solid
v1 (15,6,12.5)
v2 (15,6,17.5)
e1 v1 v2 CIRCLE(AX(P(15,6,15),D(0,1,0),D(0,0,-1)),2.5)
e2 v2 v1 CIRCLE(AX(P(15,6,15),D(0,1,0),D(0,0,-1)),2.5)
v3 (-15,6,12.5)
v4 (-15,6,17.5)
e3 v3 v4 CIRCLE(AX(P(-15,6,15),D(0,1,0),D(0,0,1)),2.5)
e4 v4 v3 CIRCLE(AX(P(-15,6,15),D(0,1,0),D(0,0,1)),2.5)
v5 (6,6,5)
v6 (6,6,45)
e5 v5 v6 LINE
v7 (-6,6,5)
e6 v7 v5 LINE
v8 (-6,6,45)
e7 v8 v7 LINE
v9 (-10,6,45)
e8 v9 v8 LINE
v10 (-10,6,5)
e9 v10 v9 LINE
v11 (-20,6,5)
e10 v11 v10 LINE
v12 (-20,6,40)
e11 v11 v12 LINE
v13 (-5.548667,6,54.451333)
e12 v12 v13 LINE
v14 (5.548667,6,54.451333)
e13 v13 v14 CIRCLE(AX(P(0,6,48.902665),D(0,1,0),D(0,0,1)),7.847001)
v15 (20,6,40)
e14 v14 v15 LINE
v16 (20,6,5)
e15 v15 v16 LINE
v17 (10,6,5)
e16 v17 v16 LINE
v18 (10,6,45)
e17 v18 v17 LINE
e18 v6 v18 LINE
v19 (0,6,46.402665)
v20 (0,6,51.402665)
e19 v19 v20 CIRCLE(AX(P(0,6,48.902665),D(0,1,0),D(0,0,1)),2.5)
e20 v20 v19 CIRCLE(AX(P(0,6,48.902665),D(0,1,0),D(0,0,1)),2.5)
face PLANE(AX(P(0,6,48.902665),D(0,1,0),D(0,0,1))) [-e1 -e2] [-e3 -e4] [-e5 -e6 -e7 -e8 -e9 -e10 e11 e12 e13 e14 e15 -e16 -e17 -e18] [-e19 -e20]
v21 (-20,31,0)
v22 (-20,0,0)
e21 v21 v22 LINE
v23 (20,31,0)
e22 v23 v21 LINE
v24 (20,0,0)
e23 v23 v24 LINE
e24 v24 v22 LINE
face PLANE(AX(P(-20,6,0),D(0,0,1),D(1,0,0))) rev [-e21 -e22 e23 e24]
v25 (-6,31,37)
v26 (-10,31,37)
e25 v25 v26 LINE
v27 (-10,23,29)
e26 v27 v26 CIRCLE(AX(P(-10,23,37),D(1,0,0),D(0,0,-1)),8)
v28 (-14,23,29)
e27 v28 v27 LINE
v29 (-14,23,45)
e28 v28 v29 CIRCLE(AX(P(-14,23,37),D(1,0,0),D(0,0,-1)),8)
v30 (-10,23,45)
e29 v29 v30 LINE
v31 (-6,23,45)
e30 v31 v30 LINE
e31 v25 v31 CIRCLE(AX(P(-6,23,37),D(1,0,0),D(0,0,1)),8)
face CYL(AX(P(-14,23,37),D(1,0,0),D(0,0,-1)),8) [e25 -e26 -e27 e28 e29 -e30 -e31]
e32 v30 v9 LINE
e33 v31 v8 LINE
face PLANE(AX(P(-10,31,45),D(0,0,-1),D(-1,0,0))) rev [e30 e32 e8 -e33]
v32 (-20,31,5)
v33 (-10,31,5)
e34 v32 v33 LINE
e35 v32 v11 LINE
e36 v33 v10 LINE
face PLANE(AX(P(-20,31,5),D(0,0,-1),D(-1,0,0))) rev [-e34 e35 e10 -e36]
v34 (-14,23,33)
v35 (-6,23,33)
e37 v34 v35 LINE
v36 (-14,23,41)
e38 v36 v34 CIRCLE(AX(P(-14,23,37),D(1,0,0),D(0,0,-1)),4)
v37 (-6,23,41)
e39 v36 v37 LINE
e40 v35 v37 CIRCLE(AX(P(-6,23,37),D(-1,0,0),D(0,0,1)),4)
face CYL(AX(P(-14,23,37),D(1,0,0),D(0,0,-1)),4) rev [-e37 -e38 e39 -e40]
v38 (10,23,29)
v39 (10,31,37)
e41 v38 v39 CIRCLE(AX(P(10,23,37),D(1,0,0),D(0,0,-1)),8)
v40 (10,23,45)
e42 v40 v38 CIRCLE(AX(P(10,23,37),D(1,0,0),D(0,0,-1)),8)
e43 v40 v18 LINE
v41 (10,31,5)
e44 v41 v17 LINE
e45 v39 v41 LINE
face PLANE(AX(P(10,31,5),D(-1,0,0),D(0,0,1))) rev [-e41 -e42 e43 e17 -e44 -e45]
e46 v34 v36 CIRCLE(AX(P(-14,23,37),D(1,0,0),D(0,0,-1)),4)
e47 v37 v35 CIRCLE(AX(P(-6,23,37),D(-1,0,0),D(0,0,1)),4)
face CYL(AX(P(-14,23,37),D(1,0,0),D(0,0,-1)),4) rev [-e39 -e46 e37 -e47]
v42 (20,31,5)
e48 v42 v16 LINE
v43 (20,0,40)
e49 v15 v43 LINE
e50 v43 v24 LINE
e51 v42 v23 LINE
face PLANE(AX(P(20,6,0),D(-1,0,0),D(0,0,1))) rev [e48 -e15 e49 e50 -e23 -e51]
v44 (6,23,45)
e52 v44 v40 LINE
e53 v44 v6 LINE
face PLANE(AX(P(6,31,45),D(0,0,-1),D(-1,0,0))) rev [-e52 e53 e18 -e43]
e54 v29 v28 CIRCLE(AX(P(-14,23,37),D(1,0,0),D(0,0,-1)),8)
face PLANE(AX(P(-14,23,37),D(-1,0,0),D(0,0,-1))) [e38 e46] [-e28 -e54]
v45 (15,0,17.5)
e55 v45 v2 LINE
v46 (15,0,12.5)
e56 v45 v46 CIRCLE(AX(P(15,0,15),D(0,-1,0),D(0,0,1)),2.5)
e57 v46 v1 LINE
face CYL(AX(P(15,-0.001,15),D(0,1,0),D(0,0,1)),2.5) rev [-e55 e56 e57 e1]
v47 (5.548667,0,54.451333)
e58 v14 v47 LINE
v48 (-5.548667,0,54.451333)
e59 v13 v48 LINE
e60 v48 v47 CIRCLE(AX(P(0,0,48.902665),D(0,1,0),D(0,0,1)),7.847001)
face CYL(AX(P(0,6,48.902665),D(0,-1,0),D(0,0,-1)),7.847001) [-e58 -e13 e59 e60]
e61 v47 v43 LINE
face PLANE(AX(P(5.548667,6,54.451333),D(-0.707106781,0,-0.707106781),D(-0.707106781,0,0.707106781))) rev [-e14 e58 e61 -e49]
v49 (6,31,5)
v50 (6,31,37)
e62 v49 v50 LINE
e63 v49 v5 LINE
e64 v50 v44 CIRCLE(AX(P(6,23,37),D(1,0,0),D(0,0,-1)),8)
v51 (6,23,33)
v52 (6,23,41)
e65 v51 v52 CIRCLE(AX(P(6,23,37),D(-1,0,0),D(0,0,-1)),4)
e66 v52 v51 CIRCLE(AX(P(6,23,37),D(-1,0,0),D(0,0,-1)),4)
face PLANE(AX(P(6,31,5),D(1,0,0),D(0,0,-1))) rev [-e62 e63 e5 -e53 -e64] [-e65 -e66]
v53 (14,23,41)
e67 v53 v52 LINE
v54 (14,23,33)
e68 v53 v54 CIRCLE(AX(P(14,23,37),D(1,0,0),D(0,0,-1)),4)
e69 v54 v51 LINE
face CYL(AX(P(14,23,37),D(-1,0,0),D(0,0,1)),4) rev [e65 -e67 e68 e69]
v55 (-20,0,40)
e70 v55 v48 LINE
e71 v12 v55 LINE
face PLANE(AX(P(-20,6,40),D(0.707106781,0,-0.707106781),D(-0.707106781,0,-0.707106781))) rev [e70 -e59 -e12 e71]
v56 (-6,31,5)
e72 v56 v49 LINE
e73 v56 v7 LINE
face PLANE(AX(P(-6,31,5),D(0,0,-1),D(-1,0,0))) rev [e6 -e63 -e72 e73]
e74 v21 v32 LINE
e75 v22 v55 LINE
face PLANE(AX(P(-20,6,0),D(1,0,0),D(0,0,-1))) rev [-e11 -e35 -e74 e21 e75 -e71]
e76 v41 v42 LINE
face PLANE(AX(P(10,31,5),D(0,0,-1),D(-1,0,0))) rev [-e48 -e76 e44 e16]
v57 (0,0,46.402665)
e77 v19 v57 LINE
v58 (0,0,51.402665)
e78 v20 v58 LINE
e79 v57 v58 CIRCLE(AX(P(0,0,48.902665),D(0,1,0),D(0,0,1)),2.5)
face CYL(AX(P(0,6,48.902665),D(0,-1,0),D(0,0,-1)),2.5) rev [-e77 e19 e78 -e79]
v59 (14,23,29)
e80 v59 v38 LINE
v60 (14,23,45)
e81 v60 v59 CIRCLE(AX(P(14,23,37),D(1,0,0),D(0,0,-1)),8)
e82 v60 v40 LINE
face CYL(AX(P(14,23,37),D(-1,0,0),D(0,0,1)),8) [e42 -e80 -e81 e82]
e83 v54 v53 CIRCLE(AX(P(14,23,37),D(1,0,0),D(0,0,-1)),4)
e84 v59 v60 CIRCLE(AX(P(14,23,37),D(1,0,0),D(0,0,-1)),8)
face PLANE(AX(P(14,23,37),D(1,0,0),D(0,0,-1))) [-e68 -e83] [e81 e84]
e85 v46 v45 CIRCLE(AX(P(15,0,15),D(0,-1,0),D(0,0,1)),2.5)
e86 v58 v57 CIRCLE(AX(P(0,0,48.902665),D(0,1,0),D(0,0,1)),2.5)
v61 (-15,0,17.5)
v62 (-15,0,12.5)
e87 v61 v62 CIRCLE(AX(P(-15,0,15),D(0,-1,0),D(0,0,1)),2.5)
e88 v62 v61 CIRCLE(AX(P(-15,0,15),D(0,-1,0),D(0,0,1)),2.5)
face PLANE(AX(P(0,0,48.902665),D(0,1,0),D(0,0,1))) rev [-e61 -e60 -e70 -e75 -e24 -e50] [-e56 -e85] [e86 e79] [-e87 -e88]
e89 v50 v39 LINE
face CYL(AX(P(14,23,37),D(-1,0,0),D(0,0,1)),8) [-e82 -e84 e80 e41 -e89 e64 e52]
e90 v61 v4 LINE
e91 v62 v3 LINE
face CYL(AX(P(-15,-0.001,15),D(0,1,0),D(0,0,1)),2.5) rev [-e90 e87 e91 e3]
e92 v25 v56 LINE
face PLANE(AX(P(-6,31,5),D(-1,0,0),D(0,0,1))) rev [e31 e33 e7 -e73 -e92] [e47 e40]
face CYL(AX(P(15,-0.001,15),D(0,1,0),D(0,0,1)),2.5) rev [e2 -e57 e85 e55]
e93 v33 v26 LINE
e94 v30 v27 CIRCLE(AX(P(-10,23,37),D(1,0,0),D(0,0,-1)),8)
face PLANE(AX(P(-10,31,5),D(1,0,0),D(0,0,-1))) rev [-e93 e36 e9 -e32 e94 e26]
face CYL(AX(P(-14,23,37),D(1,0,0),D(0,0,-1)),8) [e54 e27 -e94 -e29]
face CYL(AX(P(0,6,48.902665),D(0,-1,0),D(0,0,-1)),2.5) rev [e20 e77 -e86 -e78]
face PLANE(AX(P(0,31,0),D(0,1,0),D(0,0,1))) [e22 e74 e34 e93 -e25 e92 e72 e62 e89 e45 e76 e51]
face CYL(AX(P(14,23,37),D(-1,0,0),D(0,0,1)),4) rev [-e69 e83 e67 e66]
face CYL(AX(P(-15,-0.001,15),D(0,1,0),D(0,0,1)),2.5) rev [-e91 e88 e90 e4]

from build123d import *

# Parameters (mm, degrees)
BASE_PLATE_SKETCH_R             = 2.5
POINTED_BASE_PLATE_DEPTH        = 6
BACK_WALL_AND_CLEVIS_LUGS_DEPTH = 25
LUG_BOSS_SKETCH_R               = 8
LUG_BOSS_SKETCH_R_2             = 4
LUG_BOSS_DEPTH                  = 4
PIN_HOLE_REACH                  = 75.058
PIN_HOLE_SKETCH_R               = 4
BASE_MOUNTING_HOLES_REACH       = 67.158
MOUNTING_HOLES_SKETCH_R         = 2.5


with BuildPart() as part:
    # Base Plate Sketch → Pointed Base Plate (new body)
    with BuildSketch(Plane(origin=(0, 0, 0), x_dir=(1, 0, 0), z_dir=(0, 1, 0))):
        with BuildLine():
            Line((-20, 0), (20, 0))
            Line((20, 0), (20, -40))
            Line((20, -40), (5.548667415, -54.451332585))
            ThreePointArc((5.548667415, -54.451332585), (0, -56.749665881), (-5.548667415, -54.451332585))
            Line((-5.548667415, -54.451332585), (-20, -40))
            Line((-20, -40), (-20, 0))
        make_face()
        with Locations(Location((0, -48.902665169, 0), (0, 0, 270))):
            Circle(BASE_PLATE_SKETCH_R, mode=Mode.SUBTRACT)
    extrude(amount=POINTED_BASE_PLATE_DEPTH)

    # Back Wall and Lugs Sketch → Back Wall and Clevis Lugs (add)
    with BuildSketch(Plane(origin=(0, 6, 0), x_dir=(1, 0, 0), z_dir=(0, 1, 0))):
        Polygon((-20, 0), (20, 0), (20, -5), (10, -5), (10, -45), (6, -45), (6, -5), (-6, -5), (-6, -45), (-10, -45), (-10, -5), (-20, -5), align=None)
    extrude(amount=BACK_WALL_AND_CLEVIS_LUGS_DEPTH)

    # Lug Boss Sketch → Lug Boss (add)
    with BuildSketch(Plane(origin=(10, 0, 0), x_dir=(0, 0, -1), z_dir=(1, 0, 0))):
        with Locations(Location((-37, 23, 0), (0, 0, 180))):
            Circle(LUG_BOSS_SKETCH_R)
        with Locations((-37, 23)):
            Circle(LUG_BOSS_SKETCH_R_2, mode=Mode.SUBTRACT)
    lug_boss = extrude(amount=LUG_BOSS_DEPTH)

    # Pin Hole Sketch → Pin Hole (cut, up to next)
    with BuildSketch(Plane(origin=(14, 0, 0), x_dir=(0, 0, -1), z_dir=(1, 0, 0)), mode=Mode.PRIVATE) as pin_hole_sk1:
        with Locations((-37, 23)):
            Circle(PIN_HOLE_SKETCH_R)
    pin_hole_tool1 = extrude(pin_hole_sk1.sketch, amount=-PIN_HOLE_REACH, mode=Mode.PRIVATE) & part.part
    # Pin Hole Sketch → Pin Hole (cut, up to next)
    with BuildSketch(Plane(origin=(14, 0, 0), x_dir=(0, 0, -1), z_dir=(1, 0, 0)), mode=Mode.PRIVATE) as pin_hole_sk2:
        with BuildLine():
            Line((-45, 31), (-45, 23))
            ThreePointArc((-45, 23), (-42.656854249, 28.656854249), (-37, 31))
            Line((-37, 31), (-45, 31))
        make_face()
    pin_hole_tool2 = extrude(pin_hole_sk2.sketch, amount=-PIN_HOLE_REACH, mode=Mode.PRIVATE) & part.part
    pin_hole_1 = pin_hole_tool1.solids().sort_by_distance((14, 23, 37))[0]
    add(pin_hole_1, mode=Mode.SUBTRACT)
    pin_hole_2 = pin_hole_tool2.solids().sort_by_distance((14, 29.213056, 43.213056))[0]
    add(pin_hole_2, mode=Mode.SUBTRACT)
    pin_hole = pin_hole_1 + pin_hole_2  # Pin Hole as one shape, for the pattern or mirror that repeats it

    # Lug Boss and Pin Hole Mirror: Lug Boss, Pin Hole across plane
    add(lug_boss.mirror(Plane(origin=(0, 0, 0), x_dir=(0, 0, 1), z_dir=(1, 0, 0))))
    add(pin_hole.mirror(Plane(origin=(0, 0, 0), x_dir=(0, 0, 1), z_dir=(1, 0, 0))), mode=Mode.SUBTRACT)

    # Mounting Holes Sketch → Base Mounting Holes (cut, up to next)
    with BuildSketch(Plane(origin=(0, 6, 0), x_dir=(1, 0, 0), z_dir=(0, 1, 0)), mode=Mode.PRIVATE) as base_mounting_holes_sk1:
        with Locations(Location((-15, -15, 0), (0, 0, 270))):
            Circle(MOUNTING_HOLES_SKETCH_R)
    base_mounting_holes_tool1 = extrude(base_mounting_holes_sk1.sketch, amount=-BASE_MOUNTING_HOLES_REACH, mode=Mode.PRIVATE) & part.part
    # Mounting Holes Sketch → Base Mounting Holes (cut, up to next)
    with BuildSketch(Plane(origin=(0, 6, 0), x_dir=(1, 0, 0), z_dir=(0, 1, 0)), mode=Mode.PRIVATE) as base_mounting_holes_sk2:
        with Locations(Location((15, -15, 0), (0, 0, 270))):
            Circle(MOUNTING_HOLES_SKETCH_R)
    base_mounting_holes_tool2 = extrude(base_mounting_holes_sk2.sketch, amount=-BASE_MOUNTING_HOLES_REACH, mode=Mode.PRIVATE) & part.part
    add(base_mounting_holes_tool1.solids().sort_by_distance((-15, 6, 15))[0], mode=Mode.SUBTRACT)
    add(base_mounting_holes_tool2.solids().sort_by_distance((15, 6, 15))[0], mode=Mode.SUBTRACT)


solid = part.part
